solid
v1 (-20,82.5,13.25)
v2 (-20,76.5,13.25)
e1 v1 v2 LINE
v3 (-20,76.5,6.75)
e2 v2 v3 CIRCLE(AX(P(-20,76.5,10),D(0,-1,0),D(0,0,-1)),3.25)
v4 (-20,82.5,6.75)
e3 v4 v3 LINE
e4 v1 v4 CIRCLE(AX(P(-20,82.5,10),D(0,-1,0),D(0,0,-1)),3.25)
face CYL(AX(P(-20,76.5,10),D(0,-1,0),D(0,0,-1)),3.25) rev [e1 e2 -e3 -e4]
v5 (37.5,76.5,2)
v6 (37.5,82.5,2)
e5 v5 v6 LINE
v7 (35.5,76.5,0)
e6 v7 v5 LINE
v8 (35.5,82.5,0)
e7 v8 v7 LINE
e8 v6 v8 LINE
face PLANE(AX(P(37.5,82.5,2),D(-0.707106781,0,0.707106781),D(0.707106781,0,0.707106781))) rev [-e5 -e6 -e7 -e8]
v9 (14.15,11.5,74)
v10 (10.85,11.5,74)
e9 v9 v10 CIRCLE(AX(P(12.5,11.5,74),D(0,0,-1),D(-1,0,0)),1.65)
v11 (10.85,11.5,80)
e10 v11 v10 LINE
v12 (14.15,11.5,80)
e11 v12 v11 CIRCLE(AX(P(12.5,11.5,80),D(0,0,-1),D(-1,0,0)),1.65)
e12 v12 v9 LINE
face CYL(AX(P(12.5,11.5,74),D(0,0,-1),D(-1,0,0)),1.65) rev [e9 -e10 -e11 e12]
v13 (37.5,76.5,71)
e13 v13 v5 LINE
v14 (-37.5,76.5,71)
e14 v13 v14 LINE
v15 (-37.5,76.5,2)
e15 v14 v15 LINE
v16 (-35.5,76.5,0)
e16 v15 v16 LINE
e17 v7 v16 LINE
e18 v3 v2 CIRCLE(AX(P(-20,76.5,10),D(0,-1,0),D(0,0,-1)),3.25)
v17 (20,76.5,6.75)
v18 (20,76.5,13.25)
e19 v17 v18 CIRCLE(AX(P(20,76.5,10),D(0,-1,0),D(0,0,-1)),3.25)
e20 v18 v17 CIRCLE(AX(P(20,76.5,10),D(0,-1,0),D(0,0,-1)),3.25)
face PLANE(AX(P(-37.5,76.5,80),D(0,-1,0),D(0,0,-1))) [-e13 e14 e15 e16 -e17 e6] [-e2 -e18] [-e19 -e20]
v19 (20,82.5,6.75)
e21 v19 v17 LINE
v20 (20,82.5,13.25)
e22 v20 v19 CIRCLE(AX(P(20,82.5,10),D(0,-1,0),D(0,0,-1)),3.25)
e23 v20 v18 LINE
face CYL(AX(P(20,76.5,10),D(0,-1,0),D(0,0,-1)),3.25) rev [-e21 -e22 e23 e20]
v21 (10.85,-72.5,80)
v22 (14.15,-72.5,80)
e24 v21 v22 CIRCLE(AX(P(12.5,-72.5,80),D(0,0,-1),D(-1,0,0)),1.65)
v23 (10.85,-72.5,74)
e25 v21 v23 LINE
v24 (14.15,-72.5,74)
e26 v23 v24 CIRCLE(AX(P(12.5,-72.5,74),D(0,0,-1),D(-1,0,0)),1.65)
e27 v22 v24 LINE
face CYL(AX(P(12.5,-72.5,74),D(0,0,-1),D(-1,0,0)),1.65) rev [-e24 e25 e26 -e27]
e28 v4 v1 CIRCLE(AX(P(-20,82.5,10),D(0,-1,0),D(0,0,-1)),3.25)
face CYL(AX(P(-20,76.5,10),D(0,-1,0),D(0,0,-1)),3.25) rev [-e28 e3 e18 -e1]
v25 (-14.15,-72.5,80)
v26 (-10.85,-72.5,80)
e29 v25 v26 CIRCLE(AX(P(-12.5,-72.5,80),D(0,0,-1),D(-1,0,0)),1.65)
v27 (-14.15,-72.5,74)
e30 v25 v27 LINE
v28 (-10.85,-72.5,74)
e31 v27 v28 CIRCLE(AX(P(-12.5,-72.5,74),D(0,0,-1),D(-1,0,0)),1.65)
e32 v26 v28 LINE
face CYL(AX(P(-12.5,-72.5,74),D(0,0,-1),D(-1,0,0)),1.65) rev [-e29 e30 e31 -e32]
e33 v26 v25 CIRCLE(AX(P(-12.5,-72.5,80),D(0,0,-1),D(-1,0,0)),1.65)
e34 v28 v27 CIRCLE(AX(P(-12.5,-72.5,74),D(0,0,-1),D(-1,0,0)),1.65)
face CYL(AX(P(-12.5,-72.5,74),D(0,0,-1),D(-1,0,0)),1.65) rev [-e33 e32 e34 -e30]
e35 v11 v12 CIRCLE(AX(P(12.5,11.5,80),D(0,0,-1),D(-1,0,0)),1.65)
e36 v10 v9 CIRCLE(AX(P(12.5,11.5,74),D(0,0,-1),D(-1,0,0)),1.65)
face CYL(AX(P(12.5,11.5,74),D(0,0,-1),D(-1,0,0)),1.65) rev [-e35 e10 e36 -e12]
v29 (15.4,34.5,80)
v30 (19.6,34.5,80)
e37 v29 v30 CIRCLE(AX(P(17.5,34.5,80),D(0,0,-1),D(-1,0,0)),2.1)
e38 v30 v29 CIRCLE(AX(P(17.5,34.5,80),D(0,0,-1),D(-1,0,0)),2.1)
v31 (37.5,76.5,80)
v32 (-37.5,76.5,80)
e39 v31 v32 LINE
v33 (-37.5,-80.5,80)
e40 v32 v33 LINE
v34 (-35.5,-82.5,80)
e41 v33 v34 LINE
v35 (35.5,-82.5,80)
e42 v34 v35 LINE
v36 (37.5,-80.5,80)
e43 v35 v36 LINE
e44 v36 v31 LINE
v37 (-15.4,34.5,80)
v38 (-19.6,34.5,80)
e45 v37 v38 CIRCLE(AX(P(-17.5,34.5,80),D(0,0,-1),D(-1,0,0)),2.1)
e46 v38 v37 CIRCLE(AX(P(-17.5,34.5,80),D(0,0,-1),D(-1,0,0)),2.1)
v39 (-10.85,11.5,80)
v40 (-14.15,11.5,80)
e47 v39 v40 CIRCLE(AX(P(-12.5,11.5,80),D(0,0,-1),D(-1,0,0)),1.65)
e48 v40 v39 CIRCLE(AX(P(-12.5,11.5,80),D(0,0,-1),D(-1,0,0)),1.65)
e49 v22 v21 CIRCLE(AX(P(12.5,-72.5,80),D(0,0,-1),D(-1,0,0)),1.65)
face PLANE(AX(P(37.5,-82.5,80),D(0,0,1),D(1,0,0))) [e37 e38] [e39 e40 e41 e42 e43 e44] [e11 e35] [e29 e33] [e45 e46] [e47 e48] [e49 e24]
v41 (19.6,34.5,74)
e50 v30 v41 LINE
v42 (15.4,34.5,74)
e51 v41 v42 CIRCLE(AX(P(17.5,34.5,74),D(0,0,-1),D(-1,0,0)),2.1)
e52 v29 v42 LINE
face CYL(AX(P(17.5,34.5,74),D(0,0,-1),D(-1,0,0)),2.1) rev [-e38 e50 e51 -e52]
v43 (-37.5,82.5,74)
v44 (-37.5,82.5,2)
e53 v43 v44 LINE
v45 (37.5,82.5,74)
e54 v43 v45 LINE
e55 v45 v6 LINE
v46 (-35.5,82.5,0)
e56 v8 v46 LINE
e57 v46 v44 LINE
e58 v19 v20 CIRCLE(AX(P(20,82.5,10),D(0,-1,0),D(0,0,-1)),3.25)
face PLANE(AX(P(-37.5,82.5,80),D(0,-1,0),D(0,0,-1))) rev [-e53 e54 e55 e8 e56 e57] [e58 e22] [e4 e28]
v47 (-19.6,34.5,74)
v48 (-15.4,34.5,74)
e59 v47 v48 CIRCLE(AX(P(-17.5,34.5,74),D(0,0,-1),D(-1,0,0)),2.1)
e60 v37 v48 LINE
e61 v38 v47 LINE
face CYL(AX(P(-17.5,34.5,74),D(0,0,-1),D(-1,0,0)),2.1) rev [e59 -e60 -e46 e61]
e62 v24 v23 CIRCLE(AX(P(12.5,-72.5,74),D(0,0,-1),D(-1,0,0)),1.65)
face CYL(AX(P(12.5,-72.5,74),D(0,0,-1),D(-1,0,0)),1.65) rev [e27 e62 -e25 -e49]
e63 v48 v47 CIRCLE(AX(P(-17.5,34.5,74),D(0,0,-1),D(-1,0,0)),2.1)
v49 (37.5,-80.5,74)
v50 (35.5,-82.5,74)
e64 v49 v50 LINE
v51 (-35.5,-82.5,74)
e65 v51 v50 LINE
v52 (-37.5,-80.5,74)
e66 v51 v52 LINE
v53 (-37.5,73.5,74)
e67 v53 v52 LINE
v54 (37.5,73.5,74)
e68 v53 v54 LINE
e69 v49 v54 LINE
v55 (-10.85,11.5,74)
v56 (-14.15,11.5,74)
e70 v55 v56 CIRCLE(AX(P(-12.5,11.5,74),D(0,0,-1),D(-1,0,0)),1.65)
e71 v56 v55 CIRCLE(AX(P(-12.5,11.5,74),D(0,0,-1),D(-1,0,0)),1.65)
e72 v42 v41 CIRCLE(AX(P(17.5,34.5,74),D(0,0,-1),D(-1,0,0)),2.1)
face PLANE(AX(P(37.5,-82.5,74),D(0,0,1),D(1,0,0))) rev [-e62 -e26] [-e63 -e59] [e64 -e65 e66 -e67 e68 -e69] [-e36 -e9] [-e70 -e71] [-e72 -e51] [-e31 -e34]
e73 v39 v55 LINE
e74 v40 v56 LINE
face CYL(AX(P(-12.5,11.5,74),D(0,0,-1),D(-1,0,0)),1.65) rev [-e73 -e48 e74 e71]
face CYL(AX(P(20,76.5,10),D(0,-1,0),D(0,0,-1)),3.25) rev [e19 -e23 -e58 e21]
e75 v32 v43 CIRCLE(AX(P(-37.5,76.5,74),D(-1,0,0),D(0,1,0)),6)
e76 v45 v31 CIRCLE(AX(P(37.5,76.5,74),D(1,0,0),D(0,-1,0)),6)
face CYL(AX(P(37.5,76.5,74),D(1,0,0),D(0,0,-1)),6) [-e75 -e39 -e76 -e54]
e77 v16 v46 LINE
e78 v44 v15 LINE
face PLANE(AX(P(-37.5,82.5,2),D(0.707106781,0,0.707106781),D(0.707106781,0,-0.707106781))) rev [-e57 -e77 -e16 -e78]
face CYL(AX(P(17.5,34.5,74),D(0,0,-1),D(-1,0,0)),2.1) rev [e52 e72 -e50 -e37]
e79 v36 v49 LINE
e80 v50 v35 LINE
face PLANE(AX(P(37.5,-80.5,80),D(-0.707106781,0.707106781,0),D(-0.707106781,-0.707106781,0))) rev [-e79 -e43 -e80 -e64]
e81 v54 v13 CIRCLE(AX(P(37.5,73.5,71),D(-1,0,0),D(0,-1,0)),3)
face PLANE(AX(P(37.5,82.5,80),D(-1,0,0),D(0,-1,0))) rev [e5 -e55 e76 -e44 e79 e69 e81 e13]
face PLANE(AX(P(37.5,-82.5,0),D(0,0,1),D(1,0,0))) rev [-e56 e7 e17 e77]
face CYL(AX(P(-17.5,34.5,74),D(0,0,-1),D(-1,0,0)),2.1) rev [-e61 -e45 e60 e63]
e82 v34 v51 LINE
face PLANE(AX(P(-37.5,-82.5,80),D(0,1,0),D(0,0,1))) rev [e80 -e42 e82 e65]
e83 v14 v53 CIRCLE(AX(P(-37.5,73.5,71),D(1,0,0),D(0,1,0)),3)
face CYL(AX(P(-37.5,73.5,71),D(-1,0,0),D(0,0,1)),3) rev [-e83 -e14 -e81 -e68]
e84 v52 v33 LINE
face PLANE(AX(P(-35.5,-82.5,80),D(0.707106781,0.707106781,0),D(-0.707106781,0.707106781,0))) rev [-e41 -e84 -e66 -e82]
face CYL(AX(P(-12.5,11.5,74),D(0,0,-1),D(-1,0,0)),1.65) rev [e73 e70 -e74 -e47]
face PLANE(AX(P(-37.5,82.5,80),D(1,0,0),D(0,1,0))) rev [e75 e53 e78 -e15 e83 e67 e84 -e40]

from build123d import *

# Parameters (mm, degrees)
SKETCH1_W                      = 75
SKETCH1_H                      = 165
BOSS_EXTRUDE1_DEPTH            = 80
SHELL1_T                       = -6
FILLET1_R                      = 6
FILLET2_R                      = 3
CHAMFER1_SIZE                  = 2
M4_TAPPED_HOLE1_D              = 3.3
F_6_5_6_5_DIAMETER_HOLE1_D     = 6.5
F_6_5_6_5_DIAMETER_HOLE1_DEPTH = 10
F_6_5_6_5_DIAMETER_HOLE1_TIP   = 1.952797012
M5_TAPPED_HOLE1_D              = 4.2


with BuildPart() as part:
    # Sketch1 → Boss-Extrude1 (new body)
    with BuildSketch(Plane.XY):
        Rectangle(SKETCH1_W, SKETCH1_H)
    extrude(amount=BOSS_EXTRUDE1_DEPTH)

    # Shell1
    shell1_openings = [part.faces().sort_by_distance(p)[0] for p in [
        (0, 0, 0),
        (0, -82.5, 40),
        (-37.5, 0, 40),
        (37.5, 0, 40),
    ]]
    offset(amount=SHELL1_T, openings=shell1_openings, kind=Kind.INTERSECTION)

    # Fillet1
    fillet1_edges = [part.edges().sort_by_distance(p)[0] for p in [
        (0, 82.5, 80),
    ]]
    fillet(fillet1_edges, radius=FILLET1_R)

    # Fillet2
    fillet2_edges = [part.edges().sort_by_distance(p)[0] for p in [
        (0, 76.5, 74),
    ]]
    fillet(fillet2_edges, radius=FILLET2_R)

    # Chamfer1
    chamfer1_edges = [part.edges().sort_by_distance(p)[0] for p in [
        (-37.5, 79.5, 0),
        (37.5, 79.5, 0),
        (37.5, -82.5, 77),
        (-37.5, -82.5, 77),
    ]]
    chamfer(chamfer1_edges, length=CHAMFER1_SIZE)

    # M4 Tapped Hole1 (through all)
    with Locations(Plane(origin=(0, 0, 74), x_dir=(-1, 0, 0), z_dir=(0, 0, -1))):
        with Locations((-12.5, -72.5), (-12.5, 11.5), (12.5, 11.5), (12.5, -72.5)):
            Hole(M4_TAPPED_HOLE1_D / 2)

    # Ø6.5 (6.5) Diameter Hole1
    with Locations(Plane.XZ.offset(-76.5)):
        with Locations((-20, 10), (20, 10)):
            Hole(F_6_5_6_5_DIAMETER_HOLE1_D / 2, depth=F_6_5_6_5_DIAMETER_HOLE1_DEPTH)
            with Locations((0, 0, -(F_6_5_6_5_DIAMETER_HOLE1_DEPTH + F_6_5_6_5_DIAMETER_HOLE1_TIP / 2))):  # 118° drill point
                Cone(0, F_6_5_6_5_DIAMETER_HOLE1_D / 2, F_6_5_6_5_DIAMETER_HOLE1_TIP, mode=Mode.SUBTRACT)

    # M5 Tapped Hole1 (through all)
    with Locations(Plane(origin=(0, 0, 74), x_dir=(-1, 0, 0), z_dir=(0, 0, -1))):
        with Locations((-17.5, 34.5), (17.5, 34.5)):
            Hole(M5_TAPPED_HOLE1_D / 2)


solid = part.part
